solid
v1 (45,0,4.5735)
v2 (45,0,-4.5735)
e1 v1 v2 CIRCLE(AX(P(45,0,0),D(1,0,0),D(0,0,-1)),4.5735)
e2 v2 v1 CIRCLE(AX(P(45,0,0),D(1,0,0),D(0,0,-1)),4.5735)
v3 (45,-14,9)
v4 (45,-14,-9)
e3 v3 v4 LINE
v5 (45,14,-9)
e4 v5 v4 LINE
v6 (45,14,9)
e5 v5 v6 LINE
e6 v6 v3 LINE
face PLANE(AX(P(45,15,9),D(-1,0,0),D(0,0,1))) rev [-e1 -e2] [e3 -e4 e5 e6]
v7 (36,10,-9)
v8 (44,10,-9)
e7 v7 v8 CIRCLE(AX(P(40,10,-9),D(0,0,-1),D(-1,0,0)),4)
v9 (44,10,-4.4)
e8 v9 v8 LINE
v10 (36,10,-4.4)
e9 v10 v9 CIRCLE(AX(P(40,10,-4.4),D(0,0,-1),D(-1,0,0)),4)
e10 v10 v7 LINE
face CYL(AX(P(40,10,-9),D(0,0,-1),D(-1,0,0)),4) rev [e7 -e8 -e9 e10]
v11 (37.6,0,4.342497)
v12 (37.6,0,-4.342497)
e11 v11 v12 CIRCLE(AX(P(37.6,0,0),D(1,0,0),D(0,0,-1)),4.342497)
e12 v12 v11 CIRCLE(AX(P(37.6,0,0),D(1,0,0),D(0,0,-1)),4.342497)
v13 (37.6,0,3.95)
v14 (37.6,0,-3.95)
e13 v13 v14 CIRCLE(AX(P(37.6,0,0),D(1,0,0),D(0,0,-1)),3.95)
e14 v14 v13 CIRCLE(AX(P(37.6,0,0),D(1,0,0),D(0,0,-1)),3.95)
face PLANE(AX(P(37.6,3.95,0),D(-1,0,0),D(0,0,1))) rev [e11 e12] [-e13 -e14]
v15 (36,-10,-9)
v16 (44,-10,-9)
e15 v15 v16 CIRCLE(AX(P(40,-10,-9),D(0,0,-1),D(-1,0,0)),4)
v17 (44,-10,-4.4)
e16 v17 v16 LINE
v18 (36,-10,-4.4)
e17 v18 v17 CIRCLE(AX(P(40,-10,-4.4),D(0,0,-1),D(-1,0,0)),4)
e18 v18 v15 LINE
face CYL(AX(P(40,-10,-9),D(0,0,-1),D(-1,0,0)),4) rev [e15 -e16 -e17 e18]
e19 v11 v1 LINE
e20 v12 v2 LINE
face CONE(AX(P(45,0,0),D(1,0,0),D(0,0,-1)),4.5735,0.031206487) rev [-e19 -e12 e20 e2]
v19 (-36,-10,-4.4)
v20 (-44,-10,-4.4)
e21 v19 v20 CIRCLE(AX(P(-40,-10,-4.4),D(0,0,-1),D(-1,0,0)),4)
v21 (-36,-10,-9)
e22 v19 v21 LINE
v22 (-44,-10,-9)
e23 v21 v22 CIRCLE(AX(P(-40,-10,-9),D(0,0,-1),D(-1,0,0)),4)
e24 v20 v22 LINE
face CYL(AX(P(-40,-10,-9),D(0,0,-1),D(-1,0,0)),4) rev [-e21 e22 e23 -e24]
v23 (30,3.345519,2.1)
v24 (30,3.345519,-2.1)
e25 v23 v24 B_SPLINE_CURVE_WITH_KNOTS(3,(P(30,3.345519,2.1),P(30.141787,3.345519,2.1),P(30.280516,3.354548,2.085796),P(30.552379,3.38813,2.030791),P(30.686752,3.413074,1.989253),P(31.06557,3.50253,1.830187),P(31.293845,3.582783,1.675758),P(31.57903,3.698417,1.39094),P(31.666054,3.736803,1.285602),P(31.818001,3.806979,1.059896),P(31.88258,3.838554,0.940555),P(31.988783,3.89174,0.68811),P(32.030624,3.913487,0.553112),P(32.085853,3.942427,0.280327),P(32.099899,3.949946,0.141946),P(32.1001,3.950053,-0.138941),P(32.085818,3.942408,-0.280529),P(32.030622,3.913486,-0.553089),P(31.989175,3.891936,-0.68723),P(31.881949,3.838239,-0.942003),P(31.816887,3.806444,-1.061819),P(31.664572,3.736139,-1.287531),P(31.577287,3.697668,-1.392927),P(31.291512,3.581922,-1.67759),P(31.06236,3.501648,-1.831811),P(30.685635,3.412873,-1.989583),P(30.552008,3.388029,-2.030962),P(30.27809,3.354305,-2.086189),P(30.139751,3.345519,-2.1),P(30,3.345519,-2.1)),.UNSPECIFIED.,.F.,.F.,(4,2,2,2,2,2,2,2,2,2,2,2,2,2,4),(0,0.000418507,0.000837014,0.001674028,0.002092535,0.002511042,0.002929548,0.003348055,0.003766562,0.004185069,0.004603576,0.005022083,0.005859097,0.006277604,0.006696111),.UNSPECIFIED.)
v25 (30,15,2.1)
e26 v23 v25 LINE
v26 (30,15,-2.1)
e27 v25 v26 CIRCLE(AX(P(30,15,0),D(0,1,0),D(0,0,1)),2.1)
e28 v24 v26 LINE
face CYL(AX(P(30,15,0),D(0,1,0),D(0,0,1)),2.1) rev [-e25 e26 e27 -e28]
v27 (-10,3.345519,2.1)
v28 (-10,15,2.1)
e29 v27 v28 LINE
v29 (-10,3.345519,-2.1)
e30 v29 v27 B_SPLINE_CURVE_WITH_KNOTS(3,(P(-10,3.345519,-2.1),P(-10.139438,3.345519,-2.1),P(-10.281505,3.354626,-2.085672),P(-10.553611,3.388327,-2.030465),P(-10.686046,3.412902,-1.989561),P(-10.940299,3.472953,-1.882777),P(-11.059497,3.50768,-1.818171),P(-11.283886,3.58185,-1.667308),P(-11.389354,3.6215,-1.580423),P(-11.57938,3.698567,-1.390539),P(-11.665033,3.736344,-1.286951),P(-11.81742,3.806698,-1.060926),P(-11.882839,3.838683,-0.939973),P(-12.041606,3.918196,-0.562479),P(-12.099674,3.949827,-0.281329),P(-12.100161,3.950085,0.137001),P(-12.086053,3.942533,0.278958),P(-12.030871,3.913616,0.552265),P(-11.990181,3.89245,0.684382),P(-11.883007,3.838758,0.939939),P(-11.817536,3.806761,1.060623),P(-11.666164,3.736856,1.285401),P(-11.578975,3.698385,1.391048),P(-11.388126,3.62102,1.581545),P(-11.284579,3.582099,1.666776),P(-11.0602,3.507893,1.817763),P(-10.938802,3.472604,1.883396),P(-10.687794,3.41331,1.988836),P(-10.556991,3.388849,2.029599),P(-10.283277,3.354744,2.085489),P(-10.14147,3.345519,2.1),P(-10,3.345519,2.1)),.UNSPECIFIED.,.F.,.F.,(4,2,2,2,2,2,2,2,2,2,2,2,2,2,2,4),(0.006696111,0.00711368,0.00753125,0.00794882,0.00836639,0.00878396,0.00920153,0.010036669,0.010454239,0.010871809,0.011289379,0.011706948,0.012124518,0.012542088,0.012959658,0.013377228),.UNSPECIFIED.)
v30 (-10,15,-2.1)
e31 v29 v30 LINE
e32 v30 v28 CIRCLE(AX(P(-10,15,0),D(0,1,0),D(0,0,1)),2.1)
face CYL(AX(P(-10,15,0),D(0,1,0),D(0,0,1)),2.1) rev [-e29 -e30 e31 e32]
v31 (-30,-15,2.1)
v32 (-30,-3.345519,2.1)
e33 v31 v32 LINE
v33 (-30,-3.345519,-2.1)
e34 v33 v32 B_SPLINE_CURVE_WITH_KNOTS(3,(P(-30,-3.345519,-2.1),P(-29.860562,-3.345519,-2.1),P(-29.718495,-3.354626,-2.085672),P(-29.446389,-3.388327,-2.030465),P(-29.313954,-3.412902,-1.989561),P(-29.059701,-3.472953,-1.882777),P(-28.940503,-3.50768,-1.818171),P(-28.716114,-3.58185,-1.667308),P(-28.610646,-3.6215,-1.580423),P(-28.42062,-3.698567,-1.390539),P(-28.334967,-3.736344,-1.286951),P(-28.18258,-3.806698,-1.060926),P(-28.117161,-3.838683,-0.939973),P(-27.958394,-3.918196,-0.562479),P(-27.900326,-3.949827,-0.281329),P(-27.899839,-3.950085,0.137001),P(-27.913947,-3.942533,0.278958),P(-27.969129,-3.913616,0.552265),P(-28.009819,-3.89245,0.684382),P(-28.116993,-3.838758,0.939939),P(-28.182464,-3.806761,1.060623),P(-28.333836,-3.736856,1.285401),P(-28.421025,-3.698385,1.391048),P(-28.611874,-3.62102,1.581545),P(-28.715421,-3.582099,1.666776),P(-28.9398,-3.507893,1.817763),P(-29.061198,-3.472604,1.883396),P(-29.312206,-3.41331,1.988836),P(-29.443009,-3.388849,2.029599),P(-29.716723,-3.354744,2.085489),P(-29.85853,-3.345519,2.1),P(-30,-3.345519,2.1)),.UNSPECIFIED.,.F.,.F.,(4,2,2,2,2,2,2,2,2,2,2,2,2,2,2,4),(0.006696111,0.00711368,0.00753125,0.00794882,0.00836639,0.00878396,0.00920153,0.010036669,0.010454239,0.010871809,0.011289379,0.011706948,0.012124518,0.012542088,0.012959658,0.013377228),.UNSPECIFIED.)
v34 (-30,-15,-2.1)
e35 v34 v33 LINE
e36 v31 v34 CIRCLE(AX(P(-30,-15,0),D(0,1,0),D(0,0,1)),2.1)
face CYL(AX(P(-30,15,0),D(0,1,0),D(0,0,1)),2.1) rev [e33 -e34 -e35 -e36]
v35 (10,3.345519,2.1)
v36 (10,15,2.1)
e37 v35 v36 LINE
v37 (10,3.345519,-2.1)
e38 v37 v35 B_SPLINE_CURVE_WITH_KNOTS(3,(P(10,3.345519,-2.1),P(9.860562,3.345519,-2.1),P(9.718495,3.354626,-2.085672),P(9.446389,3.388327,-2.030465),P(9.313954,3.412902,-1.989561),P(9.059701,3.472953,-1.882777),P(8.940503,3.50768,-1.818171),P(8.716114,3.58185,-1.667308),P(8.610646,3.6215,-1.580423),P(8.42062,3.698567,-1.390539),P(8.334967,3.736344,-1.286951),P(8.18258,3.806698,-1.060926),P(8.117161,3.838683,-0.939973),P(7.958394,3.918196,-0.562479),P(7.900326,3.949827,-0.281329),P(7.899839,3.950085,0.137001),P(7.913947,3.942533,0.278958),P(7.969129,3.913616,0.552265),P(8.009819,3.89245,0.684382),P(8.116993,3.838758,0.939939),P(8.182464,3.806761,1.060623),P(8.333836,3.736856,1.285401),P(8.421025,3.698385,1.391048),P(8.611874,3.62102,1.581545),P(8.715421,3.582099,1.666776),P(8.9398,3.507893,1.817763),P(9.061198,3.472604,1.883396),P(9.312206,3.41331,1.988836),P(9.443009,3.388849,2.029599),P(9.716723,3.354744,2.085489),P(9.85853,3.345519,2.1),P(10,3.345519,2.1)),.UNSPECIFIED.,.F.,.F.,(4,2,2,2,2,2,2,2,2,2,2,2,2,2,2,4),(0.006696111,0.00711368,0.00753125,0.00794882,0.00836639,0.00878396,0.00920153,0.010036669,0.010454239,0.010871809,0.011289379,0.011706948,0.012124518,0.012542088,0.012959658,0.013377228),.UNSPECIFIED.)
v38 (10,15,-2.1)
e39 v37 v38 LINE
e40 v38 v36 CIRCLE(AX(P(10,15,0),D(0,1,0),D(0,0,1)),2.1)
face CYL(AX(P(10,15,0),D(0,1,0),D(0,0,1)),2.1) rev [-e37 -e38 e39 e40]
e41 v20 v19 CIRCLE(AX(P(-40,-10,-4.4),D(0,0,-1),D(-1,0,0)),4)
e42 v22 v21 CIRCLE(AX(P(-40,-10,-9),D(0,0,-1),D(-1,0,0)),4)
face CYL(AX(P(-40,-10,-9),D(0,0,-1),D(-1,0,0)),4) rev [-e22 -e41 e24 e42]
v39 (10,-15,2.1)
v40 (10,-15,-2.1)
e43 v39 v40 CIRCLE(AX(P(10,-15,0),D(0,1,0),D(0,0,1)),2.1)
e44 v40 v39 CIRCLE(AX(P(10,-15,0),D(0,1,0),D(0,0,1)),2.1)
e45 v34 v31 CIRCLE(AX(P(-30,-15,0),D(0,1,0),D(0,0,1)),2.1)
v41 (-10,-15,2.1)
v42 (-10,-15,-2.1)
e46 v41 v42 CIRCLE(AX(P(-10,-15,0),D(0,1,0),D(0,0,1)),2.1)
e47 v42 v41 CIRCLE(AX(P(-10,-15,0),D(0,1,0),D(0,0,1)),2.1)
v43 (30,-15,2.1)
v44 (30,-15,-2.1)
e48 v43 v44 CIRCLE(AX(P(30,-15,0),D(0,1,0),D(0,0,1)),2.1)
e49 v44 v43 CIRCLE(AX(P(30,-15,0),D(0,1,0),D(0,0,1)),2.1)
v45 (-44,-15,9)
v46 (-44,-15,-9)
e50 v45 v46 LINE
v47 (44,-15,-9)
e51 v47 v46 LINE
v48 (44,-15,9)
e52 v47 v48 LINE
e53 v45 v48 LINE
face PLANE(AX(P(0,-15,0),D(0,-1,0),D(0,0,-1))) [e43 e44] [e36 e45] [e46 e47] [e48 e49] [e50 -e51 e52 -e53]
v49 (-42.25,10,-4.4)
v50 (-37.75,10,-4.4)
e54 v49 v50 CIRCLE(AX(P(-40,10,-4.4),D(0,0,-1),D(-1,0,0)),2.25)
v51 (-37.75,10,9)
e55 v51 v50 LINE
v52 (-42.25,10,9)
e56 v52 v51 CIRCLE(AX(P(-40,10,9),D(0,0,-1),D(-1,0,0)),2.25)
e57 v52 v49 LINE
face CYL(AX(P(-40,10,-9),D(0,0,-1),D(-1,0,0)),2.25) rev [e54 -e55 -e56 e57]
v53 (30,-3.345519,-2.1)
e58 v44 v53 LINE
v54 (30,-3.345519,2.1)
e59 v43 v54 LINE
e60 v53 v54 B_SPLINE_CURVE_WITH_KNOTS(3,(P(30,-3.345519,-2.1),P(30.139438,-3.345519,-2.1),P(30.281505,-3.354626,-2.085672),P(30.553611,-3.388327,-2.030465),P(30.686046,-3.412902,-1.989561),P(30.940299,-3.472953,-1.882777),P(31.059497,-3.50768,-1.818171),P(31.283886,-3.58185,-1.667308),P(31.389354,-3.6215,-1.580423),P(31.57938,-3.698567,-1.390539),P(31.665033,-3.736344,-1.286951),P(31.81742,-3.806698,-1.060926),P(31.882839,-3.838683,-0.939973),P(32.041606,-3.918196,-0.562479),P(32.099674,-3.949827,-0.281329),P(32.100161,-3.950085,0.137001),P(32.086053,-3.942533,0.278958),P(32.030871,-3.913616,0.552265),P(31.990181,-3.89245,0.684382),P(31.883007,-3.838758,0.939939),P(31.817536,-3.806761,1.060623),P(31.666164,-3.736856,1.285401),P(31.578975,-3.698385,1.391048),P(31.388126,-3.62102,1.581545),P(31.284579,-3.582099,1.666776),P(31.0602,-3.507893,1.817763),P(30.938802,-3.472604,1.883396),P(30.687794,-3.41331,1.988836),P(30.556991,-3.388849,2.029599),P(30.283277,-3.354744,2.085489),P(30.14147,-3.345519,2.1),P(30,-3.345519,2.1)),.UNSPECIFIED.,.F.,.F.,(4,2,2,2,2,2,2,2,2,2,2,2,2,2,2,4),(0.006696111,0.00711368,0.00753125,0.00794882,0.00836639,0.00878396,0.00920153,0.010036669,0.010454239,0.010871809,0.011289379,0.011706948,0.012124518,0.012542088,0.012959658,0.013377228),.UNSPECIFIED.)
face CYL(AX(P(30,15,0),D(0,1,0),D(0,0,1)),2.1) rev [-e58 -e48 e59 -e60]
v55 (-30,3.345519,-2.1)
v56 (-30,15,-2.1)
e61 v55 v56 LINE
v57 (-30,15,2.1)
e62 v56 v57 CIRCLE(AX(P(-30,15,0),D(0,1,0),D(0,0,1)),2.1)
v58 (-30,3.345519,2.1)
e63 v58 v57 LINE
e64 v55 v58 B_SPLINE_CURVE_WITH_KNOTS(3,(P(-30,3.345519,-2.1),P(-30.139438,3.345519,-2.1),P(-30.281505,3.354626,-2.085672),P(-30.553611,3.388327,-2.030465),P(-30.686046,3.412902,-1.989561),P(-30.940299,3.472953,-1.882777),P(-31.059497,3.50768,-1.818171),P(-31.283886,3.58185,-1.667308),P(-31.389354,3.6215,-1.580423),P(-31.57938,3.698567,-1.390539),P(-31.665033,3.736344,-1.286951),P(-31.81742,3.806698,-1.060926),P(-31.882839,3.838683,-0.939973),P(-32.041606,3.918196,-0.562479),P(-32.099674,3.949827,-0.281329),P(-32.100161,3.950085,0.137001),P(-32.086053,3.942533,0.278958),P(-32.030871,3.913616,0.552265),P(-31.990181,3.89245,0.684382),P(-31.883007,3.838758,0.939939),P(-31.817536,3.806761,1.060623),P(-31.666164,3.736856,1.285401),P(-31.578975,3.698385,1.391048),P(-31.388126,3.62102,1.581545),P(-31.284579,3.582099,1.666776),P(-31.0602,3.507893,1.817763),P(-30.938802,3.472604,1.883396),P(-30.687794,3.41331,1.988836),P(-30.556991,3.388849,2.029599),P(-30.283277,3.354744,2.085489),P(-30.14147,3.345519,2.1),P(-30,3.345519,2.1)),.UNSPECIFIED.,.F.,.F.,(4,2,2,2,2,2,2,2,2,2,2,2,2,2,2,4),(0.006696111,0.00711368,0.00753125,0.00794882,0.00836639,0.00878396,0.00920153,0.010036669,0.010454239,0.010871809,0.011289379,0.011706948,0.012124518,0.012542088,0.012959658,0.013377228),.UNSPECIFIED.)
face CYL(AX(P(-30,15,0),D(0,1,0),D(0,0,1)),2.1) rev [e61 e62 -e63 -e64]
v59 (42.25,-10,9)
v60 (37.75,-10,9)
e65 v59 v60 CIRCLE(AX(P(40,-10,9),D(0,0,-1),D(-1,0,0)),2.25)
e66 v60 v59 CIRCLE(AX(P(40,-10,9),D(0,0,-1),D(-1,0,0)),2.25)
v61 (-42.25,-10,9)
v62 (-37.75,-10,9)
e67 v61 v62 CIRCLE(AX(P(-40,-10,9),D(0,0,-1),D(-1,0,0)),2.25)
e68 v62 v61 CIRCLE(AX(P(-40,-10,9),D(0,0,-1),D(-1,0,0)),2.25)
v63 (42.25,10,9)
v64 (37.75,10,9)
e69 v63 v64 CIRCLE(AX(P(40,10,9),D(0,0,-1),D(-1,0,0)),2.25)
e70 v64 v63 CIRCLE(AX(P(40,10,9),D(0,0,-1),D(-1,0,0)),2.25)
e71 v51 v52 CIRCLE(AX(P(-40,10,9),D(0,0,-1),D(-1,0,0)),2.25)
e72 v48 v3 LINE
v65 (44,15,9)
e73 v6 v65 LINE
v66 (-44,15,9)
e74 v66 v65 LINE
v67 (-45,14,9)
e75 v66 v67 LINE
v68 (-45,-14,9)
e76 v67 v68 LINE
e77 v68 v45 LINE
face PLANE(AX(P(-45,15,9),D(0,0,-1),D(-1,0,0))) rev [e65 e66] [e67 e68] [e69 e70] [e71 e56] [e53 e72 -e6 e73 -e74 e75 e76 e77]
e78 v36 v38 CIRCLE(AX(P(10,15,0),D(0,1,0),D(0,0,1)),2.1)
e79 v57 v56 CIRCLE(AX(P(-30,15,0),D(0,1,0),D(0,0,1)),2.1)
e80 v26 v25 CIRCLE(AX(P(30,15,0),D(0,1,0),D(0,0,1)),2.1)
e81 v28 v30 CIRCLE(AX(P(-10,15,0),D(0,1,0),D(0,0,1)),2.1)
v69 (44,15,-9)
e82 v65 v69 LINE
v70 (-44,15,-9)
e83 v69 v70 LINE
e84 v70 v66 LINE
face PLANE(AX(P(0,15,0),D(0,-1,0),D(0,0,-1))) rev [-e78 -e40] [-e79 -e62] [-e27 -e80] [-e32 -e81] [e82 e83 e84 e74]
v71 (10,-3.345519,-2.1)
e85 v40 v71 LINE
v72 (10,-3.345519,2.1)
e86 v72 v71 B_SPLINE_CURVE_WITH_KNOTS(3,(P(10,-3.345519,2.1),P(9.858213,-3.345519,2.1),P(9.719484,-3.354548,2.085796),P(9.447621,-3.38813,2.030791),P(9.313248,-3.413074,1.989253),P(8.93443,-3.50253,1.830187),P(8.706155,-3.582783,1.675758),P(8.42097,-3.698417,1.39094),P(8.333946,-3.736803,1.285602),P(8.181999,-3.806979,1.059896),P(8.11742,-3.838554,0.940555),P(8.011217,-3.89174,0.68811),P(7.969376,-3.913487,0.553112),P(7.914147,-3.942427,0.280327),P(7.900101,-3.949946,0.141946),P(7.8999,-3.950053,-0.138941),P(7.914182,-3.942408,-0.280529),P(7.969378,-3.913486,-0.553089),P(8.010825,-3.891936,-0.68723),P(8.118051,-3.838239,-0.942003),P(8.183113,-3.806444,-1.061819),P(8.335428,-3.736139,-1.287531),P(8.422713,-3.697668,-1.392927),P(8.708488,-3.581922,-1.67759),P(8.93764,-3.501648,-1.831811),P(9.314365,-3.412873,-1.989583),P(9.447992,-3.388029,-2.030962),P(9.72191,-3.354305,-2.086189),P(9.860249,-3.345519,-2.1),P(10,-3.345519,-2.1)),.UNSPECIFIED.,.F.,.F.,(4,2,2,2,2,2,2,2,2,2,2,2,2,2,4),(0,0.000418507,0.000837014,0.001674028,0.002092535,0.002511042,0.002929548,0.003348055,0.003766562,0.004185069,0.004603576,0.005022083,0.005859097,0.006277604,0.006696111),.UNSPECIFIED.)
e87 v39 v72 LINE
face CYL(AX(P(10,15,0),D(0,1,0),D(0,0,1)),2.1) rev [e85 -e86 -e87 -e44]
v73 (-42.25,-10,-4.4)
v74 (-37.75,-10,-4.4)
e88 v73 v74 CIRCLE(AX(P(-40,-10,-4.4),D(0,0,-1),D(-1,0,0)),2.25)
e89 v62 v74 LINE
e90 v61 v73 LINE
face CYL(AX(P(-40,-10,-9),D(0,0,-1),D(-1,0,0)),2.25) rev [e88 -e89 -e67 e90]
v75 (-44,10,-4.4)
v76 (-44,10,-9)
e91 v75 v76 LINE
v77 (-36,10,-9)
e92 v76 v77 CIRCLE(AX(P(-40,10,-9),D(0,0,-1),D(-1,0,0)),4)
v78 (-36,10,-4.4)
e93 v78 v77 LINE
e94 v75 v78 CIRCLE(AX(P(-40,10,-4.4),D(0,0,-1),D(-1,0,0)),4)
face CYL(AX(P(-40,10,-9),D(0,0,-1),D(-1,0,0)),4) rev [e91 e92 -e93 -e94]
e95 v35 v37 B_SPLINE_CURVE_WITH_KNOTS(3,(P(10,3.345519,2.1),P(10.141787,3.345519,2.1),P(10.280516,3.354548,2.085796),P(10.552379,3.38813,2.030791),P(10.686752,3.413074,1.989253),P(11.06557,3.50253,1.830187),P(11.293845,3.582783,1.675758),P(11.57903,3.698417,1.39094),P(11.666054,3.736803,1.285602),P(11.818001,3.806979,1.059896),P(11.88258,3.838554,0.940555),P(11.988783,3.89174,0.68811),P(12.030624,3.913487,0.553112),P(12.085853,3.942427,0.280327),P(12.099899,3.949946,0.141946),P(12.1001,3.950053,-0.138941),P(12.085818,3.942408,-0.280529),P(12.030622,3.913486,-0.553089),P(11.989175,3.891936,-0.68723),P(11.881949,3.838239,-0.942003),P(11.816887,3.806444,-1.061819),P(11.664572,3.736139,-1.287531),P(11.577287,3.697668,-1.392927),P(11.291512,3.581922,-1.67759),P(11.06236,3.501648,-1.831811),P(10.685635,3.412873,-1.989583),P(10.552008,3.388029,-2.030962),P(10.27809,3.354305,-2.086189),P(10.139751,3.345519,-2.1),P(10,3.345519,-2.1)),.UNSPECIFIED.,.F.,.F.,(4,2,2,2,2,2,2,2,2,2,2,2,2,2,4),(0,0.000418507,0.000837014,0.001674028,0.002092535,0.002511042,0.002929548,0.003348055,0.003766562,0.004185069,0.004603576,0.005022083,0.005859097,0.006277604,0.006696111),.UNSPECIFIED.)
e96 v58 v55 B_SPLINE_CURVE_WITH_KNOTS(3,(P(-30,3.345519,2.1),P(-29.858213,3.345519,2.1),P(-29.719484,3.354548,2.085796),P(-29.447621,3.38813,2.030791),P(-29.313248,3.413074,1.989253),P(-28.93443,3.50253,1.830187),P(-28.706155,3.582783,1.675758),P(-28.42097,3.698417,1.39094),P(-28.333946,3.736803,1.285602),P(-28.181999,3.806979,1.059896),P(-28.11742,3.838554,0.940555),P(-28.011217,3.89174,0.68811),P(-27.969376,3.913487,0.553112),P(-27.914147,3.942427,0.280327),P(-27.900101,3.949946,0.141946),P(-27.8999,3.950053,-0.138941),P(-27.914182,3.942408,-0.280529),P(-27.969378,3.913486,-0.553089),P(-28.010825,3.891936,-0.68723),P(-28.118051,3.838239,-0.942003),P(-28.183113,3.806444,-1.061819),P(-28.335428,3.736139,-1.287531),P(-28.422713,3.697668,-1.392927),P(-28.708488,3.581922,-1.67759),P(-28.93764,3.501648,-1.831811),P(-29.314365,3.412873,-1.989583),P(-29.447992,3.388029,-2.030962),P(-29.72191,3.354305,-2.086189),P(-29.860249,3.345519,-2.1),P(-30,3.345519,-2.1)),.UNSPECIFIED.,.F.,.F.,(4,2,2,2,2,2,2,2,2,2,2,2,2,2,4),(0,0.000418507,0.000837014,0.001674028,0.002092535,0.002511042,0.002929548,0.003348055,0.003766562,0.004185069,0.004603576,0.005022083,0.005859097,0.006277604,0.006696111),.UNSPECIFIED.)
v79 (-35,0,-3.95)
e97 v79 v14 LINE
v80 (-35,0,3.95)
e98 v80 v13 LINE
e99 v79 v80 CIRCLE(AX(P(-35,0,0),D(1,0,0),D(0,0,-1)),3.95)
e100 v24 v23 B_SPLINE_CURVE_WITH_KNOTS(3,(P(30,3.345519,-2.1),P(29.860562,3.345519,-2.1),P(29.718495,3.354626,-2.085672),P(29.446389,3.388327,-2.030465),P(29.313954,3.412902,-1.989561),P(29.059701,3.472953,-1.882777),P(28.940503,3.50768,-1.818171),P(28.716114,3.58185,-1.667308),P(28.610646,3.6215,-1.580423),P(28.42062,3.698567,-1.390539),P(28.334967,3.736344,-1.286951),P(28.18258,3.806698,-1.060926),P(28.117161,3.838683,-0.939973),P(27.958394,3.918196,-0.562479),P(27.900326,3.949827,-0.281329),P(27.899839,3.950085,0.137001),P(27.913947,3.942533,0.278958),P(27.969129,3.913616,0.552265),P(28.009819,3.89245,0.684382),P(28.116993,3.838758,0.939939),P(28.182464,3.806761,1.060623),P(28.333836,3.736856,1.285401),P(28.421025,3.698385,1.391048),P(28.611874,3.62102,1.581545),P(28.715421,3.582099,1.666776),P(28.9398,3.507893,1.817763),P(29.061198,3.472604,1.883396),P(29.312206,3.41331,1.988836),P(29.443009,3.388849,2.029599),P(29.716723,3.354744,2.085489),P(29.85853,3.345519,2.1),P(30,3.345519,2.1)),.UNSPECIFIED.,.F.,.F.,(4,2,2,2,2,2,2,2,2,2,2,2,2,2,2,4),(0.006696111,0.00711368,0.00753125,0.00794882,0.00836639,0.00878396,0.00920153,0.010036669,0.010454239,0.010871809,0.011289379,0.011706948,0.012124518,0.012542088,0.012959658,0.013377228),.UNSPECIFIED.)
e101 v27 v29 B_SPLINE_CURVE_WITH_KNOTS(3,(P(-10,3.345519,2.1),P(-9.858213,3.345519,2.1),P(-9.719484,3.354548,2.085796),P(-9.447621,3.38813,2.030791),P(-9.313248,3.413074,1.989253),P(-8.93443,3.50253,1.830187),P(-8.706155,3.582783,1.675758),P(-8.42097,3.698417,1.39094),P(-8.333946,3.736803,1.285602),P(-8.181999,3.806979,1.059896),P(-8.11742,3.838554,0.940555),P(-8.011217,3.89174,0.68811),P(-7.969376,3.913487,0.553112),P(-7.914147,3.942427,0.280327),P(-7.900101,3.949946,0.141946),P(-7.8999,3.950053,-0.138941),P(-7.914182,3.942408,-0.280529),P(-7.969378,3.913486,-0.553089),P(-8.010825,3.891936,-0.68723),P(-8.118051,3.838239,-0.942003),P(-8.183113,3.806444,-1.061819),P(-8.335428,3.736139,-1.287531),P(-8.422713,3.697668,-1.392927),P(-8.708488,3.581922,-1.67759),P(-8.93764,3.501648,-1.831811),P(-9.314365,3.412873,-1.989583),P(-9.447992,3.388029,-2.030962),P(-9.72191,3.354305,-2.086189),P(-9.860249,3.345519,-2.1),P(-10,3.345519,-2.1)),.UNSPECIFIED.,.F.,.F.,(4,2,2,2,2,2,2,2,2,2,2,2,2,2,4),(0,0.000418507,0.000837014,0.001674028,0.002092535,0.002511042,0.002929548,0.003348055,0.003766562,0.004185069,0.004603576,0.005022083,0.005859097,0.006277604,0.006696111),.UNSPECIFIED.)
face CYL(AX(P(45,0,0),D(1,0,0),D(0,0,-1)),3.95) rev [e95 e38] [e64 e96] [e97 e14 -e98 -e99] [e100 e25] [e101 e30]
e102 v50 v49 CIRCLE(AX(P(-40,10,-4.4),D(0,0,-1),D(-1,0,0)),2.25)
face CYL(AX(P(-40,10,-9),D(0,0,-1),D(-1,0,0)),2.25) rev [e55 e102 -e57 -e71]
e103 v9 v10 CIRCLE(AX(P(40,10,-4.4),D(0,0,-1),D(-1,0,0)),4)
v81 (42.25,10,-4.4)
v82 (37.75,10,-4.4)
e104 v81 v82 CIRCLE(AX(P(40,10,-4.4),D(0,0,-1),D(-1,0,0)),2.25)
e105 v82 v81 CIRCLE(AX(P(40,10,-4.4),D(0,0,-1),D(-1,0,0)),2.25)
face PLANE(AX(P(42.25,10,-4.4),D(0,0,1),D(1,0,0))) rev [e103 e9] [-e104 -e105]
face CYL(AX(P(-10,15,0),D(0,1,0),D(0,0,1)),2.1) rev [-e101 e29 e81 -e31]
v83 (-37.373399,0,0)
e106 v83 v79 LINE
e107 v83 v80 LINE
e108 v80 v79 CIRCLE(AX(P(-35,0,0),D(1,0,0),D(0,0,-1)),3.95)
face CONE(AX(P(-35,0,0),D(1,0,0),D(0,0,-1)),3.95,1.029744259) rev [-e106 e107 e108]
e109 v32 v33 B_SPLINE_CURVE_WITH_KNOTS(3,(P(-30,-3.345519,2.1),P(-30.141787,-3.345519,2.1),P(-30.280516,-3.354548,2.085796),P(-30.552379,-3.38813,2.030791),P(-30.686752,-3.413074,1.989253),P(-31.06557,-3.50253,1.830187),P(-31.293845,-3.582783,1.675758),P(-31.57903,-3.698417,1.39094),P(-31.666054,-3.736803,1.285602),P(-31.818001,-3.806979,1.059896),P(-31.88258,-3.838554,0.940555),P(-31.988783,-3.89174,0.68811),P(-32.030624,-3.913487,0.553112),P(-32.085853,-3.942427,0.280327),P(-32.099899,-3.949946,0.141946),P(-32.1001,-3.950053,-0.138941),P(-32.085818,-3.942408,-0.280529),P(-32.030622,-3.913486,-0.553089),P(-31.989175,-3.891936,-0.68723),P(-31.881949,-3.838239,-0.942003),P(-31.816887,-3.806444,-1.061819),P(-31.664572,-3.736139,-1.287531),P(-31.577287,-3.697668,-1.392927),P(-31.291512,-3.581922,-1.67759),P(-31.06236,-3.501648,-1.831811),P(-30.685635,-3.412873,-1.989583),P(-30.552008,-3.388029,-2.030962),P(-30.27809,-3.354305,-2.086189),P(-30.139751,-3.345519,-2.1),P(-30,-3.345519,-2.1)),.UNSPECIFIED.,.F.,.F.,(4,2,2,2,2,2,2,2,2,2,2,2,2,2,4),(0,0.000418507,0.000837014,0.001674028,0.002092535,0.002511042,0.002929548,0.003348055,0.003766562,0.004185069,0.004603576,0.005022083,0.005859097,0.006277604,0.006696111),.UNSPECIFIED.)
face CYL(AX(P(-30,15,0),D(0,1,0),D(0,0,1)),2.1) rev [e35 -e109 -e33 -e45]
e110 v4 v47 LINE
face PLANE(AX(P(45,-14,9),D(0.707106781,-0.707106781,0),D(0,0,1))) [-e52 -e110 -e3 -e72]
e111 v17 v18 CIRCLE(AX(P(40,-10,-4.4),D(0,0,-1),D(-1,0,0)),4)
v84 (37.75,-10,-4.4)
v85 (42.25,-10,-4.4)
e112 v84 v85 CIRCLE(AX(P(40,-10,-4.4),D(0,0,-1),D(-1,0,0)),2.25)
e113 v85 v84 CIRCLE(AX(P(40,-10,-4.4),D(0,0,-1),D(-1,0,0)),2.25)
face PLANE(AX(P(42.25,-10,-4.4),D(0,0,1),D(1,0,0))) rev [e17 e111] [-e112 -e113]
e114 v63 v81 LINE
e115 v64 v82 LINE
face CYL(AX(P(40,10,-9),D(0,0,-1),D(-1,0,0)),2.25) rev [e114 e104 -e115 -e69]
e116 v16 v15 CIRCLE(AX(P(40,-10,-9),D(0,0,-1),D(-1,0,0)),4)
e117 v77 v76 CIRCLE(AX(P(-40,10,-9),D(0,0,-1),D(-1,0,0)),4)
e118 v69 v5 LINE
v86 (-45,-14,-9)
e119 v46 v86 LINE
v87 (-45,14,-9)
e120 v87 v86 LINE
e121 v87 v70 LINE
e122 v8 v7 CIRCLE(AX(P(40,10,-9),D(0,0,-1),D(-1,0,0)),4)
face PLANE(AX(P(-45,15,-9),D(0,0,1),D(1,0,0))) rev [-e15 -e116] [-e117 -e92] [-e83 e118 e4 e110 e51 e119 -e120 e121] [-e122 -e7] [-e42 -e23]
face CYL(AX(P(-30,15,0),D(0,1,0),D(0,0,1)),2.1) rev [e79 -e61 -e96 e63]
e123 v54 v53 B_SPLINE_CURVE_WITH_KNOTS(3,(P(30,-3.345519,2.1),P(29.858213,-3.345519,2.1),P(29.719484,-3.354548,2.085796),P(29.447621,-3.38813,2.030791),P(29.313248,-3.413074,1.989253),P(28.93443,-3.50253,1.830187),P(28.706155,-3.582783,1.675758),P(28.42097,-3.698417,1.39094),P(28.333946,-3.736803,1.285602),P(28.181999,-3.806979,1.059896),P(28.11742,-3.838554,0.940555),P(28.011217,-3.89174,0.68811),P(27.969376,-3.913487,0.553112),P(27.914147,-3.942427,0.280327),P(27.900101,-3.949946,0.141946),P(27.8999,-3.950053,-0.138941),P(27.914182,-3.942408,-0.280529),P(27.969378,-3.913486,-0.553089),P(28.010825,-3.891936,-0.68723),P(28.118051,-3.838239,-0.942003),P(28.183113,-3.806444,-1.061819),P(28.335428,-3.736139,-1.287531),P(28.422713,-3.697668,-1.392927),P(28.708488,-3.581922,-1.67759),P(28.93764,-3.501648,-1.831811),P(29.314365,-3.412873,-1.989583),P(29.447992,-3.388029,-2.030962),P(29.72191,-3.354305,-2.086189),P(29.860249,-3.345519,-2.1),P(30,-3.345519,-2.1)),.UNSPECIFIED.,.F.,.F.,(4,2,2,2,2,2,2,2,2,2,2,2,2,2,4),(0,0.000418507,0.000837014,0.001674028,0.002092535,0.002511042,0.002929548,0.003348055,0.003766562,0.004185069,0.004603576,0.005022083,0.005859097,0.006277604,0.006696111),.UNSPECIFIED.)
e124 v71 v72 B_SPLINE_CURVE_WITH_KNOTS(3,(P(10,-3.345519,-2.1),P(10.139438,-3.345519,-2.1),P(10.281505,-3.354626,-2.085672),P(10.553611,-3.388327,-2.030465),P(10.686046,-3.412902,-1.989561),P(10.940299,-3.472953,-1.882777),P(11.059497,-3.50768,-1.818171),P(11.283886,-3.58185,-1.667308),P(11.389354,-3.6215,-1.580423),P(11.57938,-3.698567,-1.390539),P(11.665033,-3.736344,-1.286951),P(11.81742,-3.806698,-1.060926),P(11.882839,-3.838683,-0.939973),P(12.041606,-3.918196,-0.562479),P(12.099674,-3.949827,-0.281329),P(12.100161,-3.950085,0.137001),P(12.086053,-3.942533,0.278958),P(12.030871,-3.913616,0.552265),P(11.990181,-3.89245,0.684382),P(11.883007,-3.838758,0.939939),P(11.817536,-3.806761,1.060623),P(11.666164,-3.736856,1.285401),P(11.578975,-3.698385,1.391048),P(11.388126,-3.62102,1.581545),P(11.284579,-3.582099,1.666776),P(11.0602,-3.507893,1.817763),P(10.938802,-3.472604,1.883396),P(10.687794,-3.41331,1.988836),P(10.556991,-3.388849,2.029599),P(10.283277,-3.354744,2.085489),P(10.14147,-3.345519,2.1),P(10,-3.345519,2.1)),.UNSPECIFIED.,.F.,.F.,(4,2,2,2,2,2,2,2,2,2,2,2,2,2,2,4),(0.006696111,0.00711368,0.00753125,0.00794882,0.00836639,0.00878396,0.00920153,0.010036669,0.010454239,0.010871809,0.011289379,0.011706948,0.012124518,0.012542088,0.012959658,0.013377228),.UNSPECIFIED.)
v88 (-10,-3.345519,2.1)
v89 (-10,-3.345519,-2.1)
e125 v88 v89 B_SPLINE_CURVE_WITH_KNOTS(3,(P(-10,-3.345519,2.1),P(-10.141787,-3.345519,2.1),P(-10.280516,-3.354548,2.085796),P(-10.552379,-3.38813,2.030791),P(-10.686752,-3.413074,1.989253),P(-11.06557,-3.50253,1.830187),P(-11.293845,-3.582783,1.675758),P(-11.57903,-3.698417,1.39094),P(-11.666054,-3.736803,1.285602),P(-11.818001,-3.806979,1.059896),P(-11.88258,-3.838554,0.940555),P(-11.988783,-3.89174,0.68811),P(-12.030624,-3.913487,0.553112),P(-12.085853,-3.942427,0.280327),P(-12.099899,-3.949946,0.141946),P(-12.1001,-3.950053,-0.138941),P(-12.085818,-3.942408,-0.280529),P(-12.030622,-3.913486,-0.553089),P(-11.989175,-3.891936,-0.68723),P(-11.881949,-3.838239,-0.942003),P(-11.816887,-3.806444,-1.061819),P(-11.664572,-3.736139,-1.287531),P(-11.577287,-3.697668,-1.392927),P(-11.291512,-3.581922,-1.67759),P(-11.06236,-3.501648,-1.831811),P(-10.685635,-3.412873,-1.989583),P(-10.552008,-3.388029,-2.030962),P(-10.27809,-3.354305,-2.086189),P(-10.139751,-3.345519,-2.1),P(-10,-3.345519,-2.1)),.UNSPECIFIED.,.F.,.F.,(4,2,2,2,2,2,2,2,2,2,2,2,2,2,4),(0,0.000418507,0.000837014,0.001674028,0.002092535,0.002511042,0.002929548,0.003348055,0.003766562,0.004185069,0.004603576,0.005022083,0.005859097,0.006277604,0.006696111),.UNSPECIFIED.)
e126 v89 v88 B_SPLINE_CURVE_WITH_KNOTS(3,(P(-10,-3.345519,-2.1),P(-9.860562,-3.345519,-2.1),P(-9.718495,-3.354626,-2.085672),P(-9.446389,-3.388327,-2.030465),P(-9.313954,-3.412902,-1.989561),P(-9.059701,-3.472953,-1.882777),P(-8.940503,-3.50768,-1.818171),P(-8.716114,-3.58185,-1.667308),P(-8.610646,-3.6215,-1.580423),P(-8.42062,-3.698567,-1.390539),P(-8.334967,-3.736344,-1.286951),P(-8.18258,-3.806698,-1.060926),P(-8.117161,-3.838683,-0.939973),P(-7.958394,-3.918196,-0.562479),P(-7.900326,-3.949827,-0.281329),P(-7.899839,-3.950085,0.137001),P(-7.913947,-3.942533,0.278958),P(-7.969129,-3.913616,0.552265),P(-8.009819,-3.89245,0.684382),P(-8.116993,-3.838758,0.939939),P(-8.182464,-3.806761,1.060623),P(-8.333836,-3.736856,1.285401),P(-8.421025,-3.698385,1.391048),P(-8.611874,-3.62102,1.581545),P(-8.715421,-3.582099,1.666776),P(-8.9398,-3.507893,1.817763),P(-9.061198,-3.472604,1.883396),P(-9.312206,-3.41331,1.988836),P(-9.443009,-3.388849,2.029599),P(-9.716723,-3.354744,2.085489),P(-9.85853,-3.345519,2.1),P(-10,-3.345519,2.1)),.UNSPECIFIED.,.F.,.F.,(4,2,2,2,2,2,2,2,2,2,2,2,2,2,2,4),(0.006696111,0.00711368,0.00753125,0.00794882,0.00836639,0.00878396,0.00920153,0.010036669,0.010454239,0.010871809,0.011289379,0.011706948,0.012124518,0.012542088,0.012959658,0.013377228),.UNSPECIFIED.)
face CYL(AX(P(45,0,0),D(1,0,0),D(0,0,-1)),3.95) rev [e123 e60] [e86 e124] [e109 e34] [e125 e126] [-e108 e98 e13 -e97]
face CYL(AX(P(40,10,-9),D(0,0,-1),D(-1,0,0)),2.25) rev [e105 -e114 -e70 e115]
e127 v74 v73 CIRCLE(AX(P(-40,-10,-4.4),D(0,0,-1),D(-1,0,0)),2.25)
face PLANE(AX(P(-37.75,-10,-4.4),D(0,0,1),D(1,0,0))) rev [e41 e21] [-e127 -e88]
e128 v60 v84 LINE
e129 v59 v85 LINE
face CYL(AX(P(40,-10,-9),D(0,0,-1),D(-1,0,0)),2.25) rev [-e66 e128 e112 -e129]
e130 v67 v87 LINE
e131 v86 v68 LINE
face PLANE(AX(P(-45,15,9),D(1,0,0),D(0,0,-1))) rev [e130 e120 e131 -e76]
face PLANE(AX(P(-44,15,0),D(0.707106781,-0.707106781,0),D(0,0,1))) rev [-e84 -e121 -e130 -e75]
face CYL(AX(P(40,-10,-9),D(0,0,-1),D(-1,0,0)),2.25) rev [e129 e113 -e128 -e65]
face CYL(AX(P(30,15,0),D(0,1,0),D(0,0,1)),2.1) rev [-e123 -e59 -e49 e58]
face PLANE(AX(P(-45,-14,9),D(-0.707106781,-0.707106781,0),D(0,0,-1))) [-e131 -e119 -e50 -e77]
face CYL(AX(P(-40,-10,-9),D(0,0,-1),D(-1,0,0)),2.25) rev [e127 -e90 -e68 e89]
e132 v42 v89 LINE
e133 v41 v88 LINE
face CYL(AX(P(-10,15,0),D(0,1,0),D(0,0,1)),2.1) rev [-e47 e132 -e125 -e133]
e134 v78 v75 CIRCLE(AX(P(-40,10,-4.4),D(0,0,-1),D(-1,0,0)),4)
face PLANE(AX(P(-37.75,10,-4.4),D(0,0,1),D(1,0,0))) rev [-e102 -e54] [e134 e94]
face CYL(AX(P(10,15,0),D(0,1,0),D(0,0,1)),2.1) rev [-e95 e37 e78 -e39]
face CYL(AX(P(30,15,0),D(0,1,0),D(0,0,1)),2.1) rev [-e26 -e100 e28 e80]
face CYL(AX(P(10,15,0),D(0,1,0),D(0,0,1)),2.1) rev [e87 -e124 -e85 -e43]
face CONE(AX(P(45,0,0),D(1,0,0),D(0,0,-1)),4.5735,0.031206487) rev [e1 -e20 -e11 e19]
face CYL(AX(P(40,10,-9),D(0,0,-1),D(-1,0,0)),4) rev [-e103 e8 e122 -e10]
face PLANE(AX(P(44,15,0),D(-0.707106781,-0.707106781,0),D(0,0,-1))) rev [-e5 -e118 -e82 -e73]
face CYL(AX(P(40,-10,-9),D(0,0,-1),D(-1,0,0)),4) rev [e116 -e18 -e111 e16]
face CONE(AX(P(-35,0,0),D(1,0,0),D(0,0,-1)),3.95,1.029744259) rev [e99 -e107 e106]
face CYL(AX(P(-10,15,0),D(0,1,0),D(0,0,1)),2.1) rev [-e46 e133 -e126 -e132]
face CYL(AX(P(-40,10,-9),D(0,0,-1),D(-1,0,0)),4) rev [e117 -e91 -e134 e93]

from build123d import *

# Parameters (mm, degrees)
SKETCH_1_W                = 90
SKETCH_1_H                = 18
EXTRUDE_1_DEPTH           = 15
HOLE_WIZARD_M5_1_D        = 4.2
HOLE_WIZARD_1_D           = 4.5
HOLE_WIZARD_1_CBORE_D     = 8
HOLE_WIZARD_1_CBORE_DEPTH = 4.6
CHAMFER_1_SIZE            = 1


with BuildPart() as part:
    # 草图1 → 凸台-拉伸1 (new, symmetric)
    with BuildSketch(Plane(origin=(0, 0, 0), x_dir=(1, 0, 0), z_dir=(0, 1, 0))):
        Rectangle(SKETCH_1_W, SKETCH_1_H)
    extrude(amount=EXTRUDE_1_DEPTH, both=True)

    # 草图4 → 1/8 Rc 螺纹孔2 (revolve, cut)
    with BuildSketch(Plane(origin=(45, 0, 0), x_dir=(0, 0, -1), z_dir=(0, 1, 0))):
        Polygon((0, 0), (0, 82.373399445), (3.95, 80), (3.95, 7.4), (4.342497004, 7.4), (4.5735, 0), align=None)
    revolve(axis=Axis((51.35, 0, 0), (-1, 0, 0)), mode=Mode.SUBTRACT)

    # M5 螺纹孔1 (through all)
    with Locations(Plane(origin=(0, 15, 0), x_dir=(1, 0, 0), z_dir=(0, 1, 0))):
        with Locations((30, 0), (10, 0), (-10, 0), (-30, 0)):
            Hole(HOLE_WIZARD_M5_1_D / 2)

    # 打孔尺寸(%根据)内六角圆柱头螺钉的类型1 (through all)
    with Locations(Plane(origin=(0, 0, -9), x_dir=(1, 0, 0), z_dir=(0, 0, -1))):
        with Locations((-40, -10), (-40, 10), (40, 10), (40, -10)):
            CounterBoreHole(HOLE_WIZARD_1_D / 2, HOLE_WIZARD_1_CBORE_D / 2, HOLE_WIZARD_1_CBORE_DEPTH)

    # 倒角1
    chamfer_1_edges = [part.edges().sort_by_distance(p)[0] for p in [
        (-45, 15, 0),
        (45, 15, 0),
        (-45, -15, 0),
        (45, -15, 0),
    ]]
    chamfer(chamfer_1_edges, length=CHAMFER_1_SIZE)


solid = part.part
